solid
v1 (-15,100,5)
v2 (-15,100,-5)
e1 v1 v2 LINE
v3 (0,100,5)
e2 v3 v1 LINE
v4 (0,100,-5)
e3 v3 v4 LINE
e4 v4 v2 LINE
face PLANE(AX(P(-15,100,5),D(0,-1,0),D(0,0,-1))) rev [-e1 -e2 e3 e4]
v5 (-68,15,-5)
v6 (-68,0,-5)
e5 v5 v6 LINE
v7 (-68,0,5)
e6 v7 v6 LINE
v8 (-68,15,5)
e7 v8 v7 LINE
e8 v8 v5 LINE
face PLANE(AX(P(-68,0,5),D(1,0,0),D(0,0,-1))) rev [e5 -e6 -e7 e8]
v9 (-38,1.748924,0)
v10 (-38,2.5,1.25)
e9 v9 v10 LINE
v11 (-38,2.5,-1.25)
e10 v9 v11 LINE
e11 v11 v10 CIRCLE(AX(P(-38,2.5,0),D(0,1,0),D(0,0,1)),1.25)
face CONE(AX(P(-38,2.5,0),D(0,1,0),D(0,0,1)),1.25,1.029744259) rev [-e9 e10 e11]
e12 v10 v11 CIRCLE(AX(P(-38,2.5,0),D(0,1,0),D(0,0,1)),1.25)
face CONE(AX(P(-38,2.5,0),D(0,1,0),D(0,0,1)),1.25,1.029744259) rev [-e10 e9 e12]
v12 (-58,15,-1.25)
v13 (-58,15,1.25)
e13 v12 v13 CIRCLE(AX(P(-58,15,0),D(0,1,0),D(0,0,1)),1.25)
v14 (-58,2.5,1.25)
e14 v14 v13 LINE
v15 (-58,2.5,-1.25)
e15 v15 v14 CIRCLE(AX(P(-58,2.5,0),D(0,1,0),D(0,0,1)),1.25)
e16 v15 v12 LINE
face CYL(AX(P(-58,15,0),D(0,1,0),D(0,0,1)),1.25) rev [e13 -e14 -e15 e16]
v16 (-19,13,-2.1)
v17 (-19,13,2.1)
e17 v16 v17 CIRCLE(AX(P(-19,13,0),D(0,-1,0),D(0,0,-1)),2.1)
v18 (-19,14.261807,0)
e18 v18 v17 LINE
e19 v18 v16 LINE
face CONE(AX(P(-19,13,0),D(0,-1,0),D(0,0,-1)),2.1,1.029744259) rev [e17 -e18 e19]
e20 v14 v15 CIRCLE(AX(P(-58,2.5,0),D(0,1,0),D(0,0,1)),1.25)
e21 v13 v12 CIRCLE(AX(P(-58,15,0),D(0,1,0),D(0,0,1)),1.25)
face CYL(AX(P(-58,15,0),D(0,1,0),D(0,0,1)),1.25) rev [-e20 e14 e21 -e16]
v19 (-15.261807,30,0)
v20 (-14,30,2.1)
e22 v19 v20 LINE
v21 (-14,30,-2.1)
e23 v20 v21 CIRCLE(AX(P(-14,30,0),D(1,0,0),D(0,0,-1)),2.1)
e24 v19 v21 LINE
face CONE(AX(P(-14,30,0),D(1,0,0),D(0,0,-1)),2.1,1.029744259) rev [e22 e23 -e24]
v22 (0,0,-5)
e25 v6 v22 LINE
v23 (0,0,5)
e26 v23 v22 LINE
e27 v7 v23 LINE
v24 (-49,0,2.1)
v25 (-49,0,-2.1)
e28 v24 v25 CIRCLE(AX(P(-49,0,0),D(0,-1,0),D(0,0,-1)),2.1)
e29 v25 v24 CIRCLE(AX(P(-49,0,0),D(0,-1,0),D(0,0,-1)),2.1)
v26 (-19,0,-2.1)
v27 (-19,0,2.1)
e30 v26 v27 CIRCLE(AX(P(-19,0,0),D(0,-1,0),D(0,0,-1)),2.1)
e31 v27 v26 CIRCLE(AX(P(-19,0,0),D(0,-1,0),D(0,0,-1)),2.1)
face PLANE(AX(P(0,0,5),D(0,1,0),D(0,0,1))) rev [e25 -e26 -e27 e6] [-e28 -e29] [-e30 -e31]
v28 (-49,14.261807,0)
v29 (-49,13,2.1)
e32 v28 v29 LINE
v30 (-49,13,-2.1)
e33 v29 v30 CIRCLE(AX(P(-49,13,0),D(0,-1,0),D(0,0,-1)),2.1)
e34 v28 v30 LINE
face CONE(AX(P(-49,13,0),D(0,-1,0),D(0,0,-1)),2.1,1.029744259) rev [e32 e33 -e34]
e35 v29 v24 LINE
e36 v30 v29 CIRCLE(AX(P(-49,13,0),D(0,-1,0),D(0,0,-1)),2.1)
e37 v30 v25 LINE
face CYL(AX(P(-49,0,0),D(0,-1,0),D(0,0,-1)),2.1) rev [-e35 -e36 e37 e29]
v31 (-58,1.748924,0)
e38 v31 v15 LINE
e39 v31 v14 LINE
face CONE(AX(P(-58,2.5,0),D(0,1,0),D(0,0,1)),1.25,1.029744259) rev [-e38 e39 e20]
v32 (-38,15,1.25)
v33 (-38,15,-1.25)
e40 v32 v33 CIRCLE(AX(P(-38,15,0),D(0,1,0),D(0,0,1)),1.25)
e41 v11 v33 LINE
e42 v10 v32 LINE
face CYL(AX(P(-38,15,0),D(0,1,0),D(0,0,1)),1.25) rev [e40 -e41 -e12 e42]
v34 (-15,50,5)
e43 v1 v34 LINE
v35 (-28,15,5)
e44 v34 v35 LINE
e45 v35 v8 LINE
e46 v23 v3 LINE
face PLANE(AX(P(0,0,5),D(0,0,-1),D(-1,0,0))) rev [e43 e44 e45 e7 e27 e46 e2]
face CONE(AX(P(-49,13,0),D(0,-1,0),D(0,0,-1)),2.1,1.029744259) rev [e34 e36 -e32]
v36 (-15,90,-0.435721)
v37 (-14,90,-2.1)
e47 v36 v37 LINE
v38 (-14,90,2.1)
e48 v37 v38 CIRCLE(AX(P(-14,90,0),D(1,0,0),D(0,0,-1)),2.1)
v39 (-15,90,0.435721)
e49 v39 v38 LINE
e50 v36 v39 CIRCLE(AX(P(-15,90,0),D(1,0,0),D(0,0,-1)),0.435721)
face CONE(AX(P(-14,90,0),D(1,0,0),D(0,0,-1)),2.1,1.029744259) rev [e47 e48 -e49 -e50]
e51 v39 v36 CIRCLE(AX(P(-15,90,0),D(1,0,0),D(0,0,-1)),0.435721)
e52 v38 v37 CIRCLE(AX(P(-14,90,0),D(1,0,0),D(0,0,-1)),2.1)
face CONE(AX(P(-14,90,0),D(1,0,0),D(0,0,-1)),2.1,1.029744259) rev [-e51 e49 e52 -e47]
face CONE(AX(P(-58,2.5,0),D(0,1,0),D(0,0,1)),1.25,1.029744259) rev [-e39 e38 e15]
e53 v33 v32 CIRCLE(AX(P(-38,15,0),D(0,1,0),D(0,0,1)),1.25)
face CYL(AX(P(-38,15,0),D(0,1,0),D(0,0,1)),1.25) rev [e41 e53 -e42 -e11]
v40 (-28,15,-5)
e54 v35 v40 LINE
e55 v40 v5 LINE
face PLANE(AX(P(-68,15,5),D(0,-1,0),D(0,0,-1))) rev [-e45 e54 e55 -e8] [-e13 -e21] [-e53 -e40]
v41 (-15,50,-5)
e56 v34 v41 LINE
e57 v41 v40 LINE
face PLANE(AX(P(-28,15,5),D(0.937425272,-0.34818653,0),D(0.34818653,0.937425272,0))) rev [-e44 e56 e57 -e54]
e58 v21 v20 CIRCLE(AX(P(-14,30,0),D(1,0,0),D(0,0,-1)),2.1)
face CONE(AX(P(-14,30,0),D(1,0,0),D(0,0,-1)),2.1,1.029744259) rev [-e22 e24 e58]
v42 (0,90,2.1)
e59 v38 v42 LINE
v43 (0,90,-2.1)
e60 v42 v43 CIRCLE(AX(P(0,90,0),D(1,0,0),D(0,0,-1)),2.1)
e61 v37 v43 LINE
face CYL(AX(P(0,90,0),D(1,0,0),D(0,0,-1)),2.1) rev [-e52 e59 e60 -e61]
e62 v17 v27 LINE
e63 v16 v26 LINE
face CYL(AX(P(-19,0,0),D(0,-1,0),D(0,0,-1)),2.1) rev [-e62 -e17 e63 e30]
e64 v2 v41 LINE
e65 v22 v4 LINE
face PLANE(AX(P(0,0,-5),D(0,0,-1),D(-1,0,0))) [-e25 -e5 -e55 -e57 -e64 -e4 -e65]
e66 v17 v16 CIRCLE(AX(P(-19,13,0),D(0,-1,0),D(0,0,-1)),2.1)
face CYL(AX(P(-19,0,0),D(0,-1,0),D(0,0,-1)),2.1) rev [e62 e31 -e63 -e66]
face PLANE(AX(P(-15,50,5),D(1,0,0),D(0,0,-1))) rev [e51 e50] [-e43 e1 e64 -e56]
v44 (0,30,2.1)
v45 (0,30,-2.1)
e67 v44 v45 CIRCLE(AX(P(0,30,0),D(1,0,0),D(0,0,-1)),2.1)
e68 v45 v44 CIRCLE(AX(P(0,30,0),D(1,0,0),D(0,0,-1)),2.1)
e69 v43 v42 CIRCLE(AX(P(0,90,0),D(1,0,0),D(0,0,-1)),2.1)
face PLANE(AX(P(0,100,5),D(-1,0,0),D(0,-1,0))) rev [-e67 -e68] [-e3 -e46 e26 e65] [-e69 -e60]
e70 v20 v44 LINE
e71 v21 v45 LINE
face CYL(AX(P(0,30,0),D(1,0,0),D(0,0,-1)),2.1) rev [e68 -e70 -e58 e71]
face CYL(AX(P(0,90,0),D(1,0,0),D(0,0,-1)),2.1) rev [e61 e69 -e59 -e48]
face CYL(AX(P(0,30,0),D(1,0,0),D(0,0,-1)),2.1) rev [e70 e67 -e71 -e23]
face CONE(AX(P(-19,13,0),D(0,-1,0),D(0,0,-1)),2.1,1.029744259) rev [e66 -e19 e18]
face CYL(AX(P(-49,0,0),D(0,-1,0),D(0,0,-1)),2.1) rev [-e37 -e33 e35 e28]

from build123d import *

# Parameters (mm, degrees)
EXTRUDE_1_DEPTH        = 5
HOLE_WIZARD_M5_1_D     = 4.2
HOLE_WIZARD_M5_1_DEPTH = 13
HOLE_WIZARD_M5_1_TIP   = 1.2618073
HOLE_WIZARD_M5_2_D     = 4.2
HOLE_WIZARD_M5_2_DEPTH = 14
HOLE_WIZARD_M5_2_TIP   = 1.2618073
HOLE_WIZARD_M3_1_D     = 2.5
HOLE_WIZARD_M3_1_DEPTH = 12.5
HOLE_WIZARD_M3_1_TIP   = 0.751075774


with BuildPart() as part:
    # 草图1 → 凸台-拉伸1 (new, symmetric)
    with BuildSketch(Plane.XY):
        Polygon((-68, 0), (-68, 15), (-28, 15), (-15, 50), (-15, 100), (0, 100), (0, 0), align=None)
    extrude(amount=EXTRUDE_1_DEPTH, both=True)

    # M5 螺纹孔1
    with Locations(Plane(origin=(0, 0, 0), x_dir=(-1, 0, 0), z_dir=(0, -1, 0))):
        with Locations((49, 0), (19, 0)):
            Hole(HOLE_WIZARD_M5_1_D / 2, depth=HOLE_WIZARD_M5_1_DEPTH)
            with Locations((0, 0, -(HOLE_WIZARD_M5_1_DEPTH + HOLE_WIZARD_M5_1_TIP / 2))):  # 118° drill point
                Cone(0, HOLE_WIZARD_M5_1_D / 2, HOLE_WIZARD_M5_1_TIP, mode=Mode.SUBTRACT)

    # M5 螺纹孔2
    with Locations(Plane(origin=(0, 0, 0), x_dir=(0, 0, -1), z_dir=(1, 0, 0))):
        with Locations((0, 30), (0, 90)):
            Hole(HOLE_WIZARD_M5_2_D / 2, depth=HOLE_WIZARD_M5_2_DEPTH)
            with Locations((0, 0, -(HOLE_WIZARD_M5_2_DEPTH + HOLE_WIZARD_M5_2_TIP / 2))):  # 118° drill point
                Cone(0, HOLE_WIZARD_M5_2_D / 2, HOLE_WIZARD_M5_2_TIP, mode=Mode.SUBTRACT)

    # M3 螺纹孔1
    with Locations(Plane(origin=(0, 15, 0), x_dir=(1, 0, 0), z_dir=(0, 1, 0))):
        with Locations((-58, 0), (-38, 0)):
            Hole(HOLE_WIZARD_M3_1_D / 2, depth=HOLE_WIZARD_M3_1_DEPTH)
            with Locations((0, 0, -(HOLE_WIZARD_M3_1_DEPTH + HOLE_WIZARD_M3_1_TIP / 2))):  # 118° drill point
                Cone(0, HOLE_WIZARD_M3_1_D / 2, HOLE_WIZARD_M3_1_TIP, mode=Mode.SUBTRACT)


solid = part.part
